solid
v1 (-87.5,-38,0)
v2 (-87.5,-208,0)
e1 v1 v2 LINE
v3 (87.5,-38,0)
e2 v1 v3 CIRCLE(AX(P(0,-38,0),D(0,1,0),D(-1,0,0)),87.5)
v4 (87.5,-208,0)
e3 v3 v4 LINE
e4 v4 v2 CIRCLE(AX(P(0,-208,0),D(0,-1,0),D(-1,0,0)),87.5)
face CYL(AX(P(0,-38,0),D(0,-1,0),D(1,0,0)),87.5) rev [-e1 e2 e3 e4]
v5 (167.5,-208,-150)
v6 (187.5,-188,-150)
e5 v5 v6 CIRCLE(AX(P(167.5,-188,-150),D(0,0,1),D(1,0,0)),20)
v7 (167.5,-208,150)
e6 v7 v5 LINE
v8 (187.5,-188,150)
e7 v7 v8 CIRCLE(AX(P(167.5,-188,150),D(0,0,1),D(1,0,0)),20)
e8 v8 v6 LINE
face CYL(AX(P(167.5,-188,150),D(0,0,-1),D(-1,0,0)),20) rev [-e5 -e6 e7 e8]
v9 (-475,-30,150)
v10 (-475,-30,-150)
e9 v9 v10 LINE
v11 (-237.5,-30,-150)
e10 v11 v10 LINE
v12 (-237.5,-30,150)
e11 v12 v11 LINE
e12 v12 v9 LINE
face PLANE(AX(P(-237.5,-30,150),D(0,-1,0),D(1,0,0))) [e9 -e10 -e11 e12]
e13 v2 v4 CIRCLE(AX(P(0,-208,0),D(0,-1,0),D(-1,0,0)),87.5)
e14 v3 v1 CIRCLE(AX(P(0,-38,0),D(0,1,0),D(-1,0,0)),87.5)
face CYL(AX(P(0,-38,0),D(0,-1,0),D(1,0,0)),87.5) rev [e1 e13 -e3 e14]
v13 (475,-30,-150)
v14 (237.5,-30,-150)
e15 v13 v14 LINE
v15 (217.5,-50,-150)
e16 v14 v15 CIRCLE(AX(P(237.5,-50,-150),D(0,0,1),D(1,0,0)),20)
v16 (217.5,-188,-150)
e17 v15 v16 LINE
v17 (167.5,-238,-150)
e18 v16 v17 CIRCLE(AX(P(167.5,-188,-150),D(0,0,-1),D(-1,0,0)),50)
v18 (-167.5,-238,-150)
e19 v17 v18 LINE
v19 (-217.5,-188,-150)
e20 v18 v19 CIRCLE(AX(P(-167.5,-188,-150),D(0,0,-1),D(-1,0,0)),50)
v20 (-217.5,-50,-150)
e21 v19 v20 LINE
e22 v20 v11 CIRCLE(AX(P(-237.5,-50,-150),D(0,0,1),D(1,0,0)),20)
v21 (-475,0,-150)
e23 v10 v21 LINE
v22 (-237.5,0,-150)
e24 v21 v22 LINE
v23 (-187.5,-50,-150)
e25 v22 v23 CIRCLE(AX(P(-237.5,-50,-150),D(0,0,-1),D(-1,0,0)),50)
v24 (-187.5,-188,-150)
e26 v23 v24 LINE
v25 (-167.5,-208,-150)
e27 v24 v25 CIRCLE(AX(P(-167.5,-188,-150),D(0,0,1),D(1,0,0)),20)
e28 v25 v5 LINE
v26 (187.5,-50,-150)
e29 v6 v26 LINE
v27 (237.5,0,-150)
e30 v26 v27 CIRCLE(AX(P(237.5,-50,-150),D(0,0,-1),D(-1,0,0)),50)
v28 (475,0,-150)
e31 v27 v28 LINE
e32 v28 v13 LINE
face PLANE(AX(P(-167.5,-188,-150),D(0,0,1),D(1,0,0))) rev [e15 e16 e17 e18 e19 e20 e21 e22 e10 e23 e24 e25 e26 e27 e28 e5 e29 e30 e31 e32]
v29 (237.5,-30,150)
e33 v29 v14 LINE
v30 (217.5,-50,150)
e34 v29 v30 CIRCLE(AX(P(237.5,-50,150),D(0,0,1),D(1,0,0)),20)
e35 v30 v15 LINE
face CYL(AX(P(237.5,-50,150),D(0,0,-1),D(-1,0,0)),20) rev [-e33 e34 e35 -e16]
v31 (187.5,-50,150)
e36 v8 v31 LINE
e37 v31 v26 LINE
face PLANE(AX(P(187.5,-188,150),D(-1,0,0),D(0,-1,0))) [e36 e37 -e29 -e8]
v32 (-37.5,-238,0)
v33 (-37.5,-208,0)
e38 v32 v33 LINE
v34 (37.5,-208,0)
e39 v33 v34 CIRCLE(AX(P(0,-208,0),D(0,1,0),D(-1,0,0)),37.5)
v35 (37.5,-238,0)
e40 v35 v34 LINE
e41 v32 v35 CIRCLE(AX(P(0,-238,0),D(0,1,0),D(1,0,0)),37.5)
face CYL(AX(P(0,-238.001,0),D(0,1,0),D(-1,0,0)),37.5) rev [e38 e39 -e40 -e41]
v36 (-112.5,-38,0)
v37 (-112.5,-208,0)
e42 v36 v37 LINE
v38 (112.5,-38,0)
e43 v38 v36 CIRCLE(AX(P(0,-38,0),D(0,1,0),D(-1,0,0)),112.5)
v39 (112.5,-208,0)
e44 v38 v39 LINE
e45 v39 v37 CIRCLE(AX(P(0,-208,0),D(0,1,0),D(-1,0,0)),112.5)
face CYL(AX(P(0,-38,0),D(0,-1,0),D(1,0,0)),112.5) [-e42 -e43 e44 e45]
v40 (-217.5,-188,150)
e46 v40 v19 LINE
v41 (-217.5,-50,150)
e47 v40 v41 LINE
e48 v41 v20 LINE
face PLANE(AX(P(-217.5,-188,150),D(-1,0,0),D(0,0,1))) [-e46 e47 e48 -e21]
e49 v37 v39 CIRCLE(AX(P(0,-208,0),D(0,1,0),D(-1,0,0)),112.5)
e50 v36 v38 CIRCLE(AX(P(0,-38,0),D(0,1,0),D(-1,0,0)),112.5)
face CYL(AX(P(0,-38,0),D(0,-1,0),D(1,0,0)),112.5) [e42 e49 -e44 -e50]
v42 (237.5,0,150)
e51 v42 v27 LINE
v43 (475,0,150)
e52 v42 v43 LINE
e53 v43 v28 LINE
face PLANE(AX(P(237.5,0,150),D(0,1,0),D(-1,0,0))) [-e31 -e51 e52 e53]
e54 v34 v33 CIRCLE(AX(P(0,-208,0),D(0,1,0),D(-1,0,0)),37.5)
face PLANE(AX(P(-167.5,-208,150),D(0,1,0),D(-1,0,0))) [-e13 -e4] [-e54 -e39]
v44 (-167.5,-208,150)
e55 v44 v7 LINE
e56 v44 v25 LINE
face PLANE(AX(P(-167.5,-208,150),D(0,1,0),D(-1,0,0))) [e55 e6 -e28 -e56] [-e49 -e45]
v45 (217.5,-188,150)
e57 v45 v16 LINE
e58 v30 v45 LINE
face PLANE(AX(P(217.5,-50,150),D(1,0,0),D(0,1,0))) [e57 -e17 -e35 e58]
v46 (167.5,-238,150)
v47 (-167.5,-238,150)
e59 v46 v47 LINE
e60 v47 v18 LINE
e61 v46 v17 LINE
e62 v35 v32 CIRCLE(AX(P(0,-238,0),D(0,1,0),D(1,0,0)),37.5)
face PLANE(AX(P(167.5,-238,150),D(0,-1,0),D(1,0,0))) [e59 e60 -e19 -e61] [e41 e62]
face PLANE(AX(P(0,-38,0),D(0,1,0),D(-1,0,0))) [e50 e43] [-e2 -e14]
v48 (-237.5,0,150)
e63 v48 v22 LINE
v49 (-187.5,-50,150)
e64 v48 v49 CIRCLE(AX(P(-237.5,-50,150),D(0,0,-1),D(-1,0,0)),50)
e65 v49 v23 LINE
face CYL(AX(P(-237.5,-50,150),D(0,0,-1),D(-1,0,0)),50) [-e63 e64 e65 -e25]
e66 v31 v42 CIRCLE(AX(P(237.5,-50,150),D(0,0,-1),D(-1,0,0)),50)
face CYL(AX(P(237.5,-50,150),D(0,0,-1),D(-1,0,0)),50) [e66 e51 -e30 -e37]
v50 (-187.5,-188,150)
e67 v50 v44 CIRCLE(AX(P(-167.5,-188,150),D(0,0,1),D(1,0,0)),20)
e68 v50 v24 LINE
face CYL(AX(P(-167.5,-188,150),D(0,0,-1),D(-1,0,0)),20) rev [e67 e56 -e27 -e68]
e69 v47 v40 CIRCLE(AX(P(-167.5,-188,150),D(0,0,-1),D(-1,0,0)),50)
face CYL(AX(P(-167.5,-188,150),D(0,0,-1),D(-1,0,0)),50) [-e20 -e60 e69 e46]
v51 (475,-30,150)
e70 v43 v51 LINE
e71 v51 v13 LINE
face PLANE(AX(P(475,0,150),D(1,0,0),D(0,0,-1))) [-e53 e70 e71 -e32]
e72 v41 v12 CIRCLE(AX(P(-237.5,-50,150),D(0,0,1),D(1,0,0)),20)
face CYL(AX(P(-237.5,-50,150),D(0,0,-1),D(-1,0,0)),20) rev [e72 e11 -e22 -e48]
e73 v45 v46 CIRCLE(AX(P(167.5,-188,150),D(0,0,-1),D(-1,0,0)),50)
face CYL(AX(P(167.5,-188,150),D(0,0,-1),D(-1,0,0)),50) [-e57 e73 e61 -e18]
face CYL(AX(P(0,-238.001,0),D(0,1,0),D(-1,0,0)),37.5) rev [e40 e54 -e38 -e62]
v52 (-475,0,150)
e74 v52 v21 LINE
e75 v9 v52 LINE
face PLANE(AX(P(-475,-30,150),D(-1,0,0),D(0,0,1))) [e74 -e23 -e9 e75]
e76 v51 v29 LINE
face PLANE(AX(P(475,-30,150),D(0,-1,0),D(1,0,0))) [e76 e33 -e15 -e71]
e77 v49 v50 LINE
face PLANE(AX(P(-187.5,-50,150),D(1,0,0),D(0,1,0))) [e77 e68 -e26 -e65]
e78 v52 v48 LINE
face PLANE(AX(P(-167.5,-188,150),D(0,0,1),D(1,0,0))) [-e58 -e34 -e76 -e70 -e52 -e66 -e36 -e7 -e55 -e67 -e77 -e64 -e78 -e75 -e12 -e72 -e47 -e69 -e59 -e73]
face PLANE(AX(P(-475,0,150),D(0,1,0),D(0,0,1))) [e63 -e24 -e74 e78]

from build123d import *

# Parameters (mm, degrees)
FORMED_BRACKET_BODY_DEPTH = 150
BOSS_TUBE_SKETCH_R        = 112.5
BOSS_TUBE_SKETCH_R_2      = 87.5
BOSS_TUBE_225X170_DEPTH   = 170
BASE_HOLE_75_REACH        = 541.805
BASE_HOLE_SKETCH_R        = 37.5


with BuildPart() as part:
    # Bracket Profile Sketch → Formed Bracket Body (new, symmetric)
    with BuildSketch(Plane.XY):
        with BuildLine():
            Line((-475, 0), (-237.5, 0))
            ThreePointArc((-237.5, 0), (-202.144660941, -14.644660941), (-187.5, -50))
            Line((-187.5, -50), (-187.5, -188))
            ThreePointArc((-187.5, -188), (-181.642135624, -202.142135624), (-167.5, -208))
            Line((-167.5, -208), (167.5, -208))
            ThreePointArc((167.5, -208), (181.642135624, -202.142135624), (187.5, -188))
            Line((187.5, -188), (187.5, -50))
            ThreePointArc((187.5, -50), (202.144660941, -14.644660941), (237.5, 0))
            Line((237.5, 0), (475, 0))
            Line((475, 0), (475, -30))
            Line((475, -30), (237.5, -30))
            ThreePointArc((237.5, -30), (223.357864376, -35.857864376), (217.5, -50))
            Line((217.5, -50), (217.5, -188))
            ThreePointArc((217.5, -188), (202.855339059, -223.355339059), (167.5, -238))
            Line((167.5, -238), (-167.5, -238))
            ThreePointArc((-167.5, -238), (-202.855339059, -223.355339059), (-217.5, -188))
            Line((-217.5, -188), (-217.5, -50))
            ThreePointArc((-217.5, -50), (-223.357864376, -35.857864376), (-237.5, -30))
            Line((-237.5, -30), (-475, -30))
            Line((-475, -30), (-475, 0))
        make_face()
    extrude(amount=FORMED_BRACKET_BODY_DEPTH, both=True)

    # Boss Tube Sketch → Boss Tube Ø225x170 (add)
    with BuildSketch(Plane(origin=(0, -208, 0), x_dir=(1, 0, 0), z_dir=(0, 1, 0))):
        with Locations(Location((0, 0, 0), (0, 0, 180))):
            Circle(BOSS_TUBE_SKETCH_R)
        with Locations(Location((0, 0, 0), (0, 0, 180))):
            Circle(BOSS_TUBE_SKETCH_R_2, mode=Mode.SUBTRACT)
    extrude(amount=BOSS_TUBE_225X170_DEPTH)

    # Base Hole Sketch → Base Hole Ø75 (cut, up to next)
    with BuildSketch(Plane(origin=(0, -208, 0), x_dir=(1, 0, 0), z_dir=(0, 1, 0)), mode=Mode.PRIVATE) as base_hole_75_sk1:
        with Locations(Location((0, 0, 0), (0, 0, 180))):
            Circle(BASE_HOLE_SKETCH_R)
    base_hole_75_tool1 = extrude(base_hole_75_sk1.sketch, amount=-BASE_HOLE_75_REACH, mode=Mode.PRIVATE) & part.part
    add(base_hole_75_tool1.solids().sort_by_distance((0, -208, 0))[0], mode=Mode.SUBTRACT)


solid = part.part
